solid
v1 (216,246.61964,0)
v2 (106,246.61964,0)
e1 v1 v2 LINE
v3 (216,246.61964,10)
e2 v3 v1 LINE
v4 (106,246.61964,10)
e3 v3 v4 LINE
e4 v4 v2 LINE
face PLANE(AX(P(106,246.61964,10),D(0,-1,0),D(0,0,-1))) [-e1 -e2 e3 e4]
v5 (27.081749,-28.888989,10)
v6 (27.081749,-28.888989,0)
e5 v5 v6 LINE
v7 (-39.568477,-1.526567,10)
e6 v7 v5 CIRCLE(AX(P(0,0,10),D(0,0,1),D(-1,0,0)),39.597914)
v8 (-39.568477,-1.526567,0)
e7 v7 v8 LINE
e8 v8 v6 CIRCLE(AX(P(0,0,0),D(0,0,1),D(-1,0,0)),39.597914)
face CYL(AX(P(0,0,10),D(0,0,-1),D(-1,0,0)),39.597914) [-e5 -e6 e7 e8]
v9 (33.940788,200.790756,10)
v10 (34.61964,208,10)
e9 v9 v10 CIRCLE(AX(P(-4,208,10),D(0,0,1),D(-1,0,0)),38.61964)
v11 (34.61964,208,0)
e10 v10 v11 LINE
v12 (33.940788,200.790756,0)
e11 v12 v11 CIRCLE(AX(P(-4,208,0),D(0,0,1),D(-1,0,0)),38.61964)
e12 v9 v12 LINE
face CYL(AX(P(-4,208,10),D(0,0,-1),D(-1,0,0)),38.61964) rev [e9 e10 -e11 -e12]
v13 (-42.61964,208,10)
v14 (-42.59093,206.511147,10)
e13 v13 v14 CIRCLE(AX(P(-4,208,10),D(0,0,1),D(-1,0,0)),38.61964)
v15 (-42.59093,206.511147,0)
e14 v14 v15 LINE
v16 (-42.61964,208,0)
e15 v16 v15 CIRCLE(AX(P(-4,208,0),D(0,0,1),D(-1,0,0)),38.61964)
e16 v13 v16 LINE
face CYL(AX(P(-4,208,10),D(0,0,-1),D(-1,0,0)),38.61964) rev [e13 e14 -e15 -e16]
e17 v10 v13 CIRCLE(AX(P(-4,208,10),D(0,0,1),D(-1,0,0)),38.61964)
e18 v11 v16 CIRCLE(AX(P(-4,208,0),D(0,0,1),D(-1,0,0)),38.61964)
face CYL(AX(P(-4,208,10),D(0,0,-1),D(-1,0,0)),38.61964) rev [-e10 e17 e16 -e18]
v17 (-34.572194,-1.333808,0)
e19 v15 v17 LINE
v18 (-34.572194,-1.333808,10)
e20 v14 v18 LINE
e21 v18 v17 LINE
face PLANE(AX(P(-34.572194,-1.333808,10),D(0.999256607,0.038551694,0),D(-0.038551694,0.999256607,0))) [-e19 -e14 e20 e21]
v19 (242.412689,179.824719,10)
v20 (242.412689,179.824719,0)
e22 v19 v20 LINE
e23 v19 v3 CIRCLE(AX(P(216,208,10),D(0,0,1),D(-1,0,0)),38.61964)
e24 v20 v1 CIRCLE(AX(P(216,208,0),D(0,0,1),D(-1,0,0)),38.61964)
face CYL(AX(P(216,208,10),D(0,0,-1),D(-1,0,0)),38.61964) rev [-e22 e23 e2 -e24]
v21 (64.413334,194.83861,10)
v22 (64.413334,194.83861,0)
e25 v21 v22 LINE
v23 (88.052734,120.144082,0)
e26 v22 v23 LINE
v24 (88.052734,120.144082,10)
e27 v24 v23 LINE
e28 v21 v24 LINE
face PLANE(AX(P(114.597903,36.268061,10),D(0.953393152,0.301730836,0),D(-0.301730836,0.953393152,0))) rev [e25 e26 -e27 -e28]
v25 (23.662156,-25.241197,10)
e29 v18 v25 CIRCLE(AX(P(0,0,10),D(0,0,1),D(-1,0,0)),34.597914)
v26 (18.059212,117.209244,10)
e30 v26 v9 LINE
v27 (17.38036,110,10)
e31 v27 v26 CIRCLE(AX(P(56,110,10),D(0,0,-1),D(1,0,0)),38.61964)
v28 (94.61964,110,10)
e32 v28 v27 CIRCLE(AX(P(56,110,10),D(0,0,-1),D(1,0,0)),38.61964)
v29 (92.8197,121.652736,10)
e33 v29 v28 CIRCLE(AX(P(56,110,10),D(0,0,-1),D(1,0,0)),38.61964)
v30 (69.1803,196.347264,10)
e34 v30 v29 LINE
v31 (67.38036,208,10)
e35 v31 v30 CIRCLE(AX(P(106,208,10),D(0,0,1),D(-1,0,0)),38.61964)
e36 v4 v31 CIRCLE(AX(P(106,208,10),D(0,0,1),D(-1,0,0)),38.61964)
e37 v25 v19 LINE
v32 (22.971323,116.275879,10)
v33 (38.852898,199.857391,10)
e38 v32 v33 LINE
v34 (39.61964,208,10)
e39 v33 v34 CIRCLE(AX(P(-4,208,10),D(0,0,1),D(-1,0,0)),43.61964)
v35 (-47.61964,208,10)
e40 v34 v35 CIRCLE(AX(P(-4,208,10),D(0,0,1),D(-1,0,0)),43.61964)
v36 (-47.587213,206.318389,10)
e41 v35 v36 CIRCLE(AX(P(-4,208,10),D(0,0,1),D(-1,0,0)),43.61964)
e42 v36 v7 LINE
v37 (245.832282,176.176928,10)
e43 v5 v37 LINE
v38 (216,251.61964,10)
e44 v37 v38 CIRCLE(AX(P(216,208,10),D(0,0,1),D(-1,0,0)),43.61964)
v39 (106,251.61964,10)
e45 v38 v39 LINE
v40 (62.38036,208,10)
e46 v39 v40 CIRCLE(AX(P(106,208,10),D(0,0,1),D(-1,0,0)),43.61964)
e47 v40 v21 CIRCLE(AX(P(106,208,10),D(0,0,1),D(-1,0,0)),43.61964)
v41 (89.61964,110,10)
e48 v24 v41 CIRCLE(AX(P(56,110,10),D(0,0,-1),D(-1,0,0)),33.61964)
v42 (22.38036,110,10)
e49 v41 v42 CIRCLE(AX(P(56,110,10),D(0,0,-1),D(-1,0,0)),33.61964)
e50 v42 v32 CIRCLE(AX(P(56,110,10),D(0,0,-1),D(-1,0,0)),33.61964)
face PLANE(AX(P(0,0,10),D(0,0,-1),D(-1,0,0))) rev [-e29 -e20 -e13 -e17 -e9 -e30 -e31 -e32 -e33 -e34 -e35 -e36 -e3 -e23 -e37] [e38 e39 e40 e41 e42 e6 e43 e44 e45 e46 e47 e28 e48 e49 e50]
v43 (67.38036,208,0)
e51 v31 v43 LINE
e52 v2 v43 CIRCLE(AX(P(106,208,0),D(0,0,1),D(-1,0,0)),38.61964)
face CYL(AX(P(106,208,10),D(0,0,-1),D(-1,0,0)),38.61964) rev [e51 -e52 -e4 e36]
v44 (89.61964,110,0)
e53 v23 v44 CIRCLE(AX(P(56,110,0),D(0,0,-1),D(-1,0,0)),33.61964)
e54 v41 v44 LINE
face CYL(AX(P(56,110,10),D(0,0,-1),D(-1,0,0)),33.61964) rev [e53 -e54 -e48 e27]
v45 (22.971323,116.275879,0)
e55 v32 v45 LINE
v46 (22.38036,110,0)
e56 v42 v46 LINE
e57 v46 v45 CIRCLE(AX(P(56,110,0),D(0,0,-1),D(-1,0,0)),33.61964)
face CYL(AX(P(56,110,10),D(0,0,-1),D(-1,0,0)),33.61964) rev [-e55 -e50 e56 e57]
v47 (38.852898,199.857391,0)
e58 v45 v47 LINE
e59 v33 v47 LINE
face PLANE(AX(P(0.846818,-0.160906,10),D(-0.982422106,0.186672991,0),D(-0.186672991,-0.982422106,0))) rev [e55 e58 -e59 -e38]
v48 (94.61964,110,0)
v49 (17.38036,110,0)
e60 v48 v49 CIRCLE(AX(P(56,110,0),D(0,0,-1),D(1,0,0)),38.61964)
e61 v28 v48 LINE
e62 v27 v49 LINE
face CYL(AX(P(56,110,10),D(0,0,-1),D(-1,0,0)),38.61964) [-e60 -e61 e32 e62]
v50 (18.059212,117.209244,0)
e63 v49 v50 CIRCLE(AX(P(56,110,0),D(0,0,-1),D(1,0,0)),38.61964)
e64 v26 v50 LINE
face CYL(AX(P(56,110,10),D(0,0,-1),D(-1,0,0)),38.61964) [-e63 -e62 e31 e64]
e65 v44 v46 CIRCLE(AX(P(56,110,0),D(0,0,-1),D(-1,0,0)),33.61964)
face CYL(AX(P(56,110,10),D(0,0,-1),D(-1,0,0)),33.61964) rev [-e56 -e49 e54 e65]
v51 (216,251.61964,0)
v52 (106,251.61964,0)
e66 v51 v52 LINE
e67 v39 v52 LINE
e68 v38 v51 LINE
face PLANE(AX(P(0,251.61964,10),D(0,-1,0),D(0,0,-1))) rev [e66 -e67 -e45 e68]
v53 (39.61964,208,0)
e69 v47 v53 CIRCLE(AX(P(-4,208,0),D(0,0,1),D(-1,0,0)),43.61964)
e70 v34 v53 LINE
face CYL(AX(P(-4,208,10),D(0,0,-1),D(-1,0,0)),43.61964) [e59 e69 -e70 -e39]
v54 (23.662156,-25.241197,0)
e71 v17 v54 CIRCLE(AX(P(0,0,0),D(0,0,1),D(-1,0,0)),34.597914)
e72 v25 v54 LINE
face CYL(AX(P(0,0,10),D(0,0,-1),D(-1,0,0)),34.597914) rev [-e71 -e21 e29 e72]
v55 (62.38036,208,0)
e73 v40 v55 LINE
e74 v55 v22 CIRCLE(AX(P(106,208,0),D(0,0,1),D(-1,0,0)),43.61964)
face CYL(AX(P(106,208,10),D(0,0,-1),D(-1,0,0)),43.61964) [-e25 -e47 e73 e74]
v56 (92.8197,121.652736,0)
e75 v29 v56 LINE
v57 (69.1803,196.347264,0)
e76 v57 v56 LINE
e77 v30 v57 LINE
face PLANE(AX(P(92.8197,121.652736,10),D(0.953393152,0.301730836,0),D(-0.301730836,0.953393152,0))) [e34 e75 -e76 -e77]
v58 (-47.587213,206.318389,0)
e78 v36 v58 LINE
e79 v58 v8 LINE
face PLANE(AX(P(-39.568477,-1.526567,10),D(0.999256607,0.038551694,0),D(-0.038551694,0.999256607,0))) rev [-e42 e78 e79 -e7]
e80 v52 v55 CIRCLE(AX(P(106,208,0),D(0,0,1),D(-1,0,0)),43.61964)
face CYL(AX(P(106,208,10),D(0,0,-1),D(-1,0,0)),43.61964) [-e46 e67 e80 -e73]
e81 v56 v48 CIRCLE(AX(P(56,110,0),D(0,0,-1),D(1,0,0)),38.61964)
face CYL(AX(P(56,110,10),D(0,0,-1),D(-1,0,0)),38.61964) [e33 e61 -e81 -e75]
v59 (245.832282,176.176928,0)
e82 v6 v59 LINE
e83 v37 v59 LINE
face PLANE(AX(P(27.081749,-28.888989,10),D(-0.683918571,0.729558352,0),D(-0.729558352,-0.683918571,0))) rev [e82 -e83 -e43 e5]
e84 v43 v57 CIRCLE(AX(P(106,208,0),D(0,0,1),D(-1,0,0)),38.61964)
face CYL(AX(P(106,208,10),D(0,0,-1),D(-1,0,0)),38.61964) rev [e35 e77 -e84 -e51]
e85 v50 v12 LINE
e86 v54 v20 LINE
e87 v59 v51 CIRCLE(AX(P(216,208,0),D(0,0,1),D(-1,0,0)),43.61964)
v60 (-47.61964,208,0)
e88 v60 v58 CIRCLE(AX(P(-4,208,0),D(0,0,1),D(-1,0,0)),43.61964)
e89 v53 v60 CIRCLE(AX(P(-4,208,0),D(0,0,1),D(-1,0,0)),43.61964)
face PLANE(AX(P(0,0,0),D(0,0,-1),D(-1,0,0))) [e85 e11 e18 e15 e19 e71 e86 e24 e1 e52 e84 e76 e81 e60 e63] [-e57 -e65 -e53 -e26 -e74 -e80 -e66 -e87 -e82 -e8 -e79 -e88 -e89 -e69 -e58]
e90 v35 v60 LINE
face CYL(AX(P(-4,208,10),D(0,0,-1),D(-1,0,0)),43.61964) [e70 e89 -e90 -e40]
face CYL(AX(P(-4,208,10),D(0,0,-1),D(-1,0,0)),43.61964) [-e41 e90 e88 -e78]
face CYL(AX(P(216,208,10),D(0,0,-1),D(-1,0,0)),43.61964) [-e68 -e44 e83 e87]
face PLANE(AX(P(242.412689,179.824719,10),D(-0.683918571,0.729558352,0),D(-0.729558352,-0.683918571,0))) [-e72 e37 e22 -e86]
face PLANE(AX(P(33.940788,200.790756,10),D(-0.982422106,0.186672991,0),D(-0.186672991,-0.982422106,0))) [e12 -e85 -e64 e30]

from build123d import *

# Parameters (mm, degrees)
EXTRUDE_1_DEPTH = 10


with BuildPart() as part:
    # 草图2 → 拉伸-薄壁1 (new body)
    with BuildSketch(Plane.XY):
        with BuildLine():
            Line((245.832281676, 176.176927505), (27.081748613, -28.88898874))
            ThreePointArc((27.081748613, -28.88898874), (-15.038455107, -36.631129472), (-39.568477007, -1.526566661))
            Line((-39.568477007, -1.526566661), (-47.587213234, 206.31838899))
            ThreePointArc((-47.587213234, 206.31838899), (-0.748703771, 251.498299345), (38.852898358, 199.857391364))
            Line((38.852898358, 199.857391364), (22.971322702, 116.275878645))
            ThreePointArc((22.971322702, 116.275878645), (57.994709331, 76.439587045), (88.052734333, 120.144081921))
            Line((88.052734333, 120.144081921), (64.413334144, 194.838609646))
            ThreePointArc((64.413334144, 194.838609646), (70.809318853, 233.773803242), (106, 251.619639764))
            Line((106, 251.619639764), (216, 251.619639764))
            ThreePointArc((216, 251.619639764), (256.563431385, 224.039981525), (245.832281676, 176.176927505))
        make_face()
        with BuildLine():
            Line((242.412688823, 179.824719264), (23.66215576, -25.241196981))
            ThreePointArc((23.66215576, -25.241196981), (-13.139560233, -32.00574319), (-34.572193971, -1.333808191))
            Line((-34.572193971, -1.333808191), (-42.590930198, 206.511147461))
            ThreePointArc((-42.590930198, 206.511147461), (-1.121390965, 246.512208266), (33.940787828, 200.790756321))
            Line((33.940787828, 200.790756321), (18.059212172, 117.209243602))
            ThreePointArc((18.059212172, 117.209243602), (58.291367675, 71.448395421), (92.819700095, 121.652736099))
            Line((92.819700095, 121.652736099), (69.180299905, 196.347263824))
            ThreePointArc((69.180299905, 196.347263824), (74.843130382, 230.819422671), (106, 246.619639764))
            Line((106, 246.619639764), (216, 246.619639764))
            ThreePointArc((216, 246.619639764), (251.913756192, 222.201362315), (242.412688823, 179.824719264))
        make_face(mode=Mode.SUBTRACT)
    extrude(amount=EXTRUDE_1_DEPTH)


solid = part.part
